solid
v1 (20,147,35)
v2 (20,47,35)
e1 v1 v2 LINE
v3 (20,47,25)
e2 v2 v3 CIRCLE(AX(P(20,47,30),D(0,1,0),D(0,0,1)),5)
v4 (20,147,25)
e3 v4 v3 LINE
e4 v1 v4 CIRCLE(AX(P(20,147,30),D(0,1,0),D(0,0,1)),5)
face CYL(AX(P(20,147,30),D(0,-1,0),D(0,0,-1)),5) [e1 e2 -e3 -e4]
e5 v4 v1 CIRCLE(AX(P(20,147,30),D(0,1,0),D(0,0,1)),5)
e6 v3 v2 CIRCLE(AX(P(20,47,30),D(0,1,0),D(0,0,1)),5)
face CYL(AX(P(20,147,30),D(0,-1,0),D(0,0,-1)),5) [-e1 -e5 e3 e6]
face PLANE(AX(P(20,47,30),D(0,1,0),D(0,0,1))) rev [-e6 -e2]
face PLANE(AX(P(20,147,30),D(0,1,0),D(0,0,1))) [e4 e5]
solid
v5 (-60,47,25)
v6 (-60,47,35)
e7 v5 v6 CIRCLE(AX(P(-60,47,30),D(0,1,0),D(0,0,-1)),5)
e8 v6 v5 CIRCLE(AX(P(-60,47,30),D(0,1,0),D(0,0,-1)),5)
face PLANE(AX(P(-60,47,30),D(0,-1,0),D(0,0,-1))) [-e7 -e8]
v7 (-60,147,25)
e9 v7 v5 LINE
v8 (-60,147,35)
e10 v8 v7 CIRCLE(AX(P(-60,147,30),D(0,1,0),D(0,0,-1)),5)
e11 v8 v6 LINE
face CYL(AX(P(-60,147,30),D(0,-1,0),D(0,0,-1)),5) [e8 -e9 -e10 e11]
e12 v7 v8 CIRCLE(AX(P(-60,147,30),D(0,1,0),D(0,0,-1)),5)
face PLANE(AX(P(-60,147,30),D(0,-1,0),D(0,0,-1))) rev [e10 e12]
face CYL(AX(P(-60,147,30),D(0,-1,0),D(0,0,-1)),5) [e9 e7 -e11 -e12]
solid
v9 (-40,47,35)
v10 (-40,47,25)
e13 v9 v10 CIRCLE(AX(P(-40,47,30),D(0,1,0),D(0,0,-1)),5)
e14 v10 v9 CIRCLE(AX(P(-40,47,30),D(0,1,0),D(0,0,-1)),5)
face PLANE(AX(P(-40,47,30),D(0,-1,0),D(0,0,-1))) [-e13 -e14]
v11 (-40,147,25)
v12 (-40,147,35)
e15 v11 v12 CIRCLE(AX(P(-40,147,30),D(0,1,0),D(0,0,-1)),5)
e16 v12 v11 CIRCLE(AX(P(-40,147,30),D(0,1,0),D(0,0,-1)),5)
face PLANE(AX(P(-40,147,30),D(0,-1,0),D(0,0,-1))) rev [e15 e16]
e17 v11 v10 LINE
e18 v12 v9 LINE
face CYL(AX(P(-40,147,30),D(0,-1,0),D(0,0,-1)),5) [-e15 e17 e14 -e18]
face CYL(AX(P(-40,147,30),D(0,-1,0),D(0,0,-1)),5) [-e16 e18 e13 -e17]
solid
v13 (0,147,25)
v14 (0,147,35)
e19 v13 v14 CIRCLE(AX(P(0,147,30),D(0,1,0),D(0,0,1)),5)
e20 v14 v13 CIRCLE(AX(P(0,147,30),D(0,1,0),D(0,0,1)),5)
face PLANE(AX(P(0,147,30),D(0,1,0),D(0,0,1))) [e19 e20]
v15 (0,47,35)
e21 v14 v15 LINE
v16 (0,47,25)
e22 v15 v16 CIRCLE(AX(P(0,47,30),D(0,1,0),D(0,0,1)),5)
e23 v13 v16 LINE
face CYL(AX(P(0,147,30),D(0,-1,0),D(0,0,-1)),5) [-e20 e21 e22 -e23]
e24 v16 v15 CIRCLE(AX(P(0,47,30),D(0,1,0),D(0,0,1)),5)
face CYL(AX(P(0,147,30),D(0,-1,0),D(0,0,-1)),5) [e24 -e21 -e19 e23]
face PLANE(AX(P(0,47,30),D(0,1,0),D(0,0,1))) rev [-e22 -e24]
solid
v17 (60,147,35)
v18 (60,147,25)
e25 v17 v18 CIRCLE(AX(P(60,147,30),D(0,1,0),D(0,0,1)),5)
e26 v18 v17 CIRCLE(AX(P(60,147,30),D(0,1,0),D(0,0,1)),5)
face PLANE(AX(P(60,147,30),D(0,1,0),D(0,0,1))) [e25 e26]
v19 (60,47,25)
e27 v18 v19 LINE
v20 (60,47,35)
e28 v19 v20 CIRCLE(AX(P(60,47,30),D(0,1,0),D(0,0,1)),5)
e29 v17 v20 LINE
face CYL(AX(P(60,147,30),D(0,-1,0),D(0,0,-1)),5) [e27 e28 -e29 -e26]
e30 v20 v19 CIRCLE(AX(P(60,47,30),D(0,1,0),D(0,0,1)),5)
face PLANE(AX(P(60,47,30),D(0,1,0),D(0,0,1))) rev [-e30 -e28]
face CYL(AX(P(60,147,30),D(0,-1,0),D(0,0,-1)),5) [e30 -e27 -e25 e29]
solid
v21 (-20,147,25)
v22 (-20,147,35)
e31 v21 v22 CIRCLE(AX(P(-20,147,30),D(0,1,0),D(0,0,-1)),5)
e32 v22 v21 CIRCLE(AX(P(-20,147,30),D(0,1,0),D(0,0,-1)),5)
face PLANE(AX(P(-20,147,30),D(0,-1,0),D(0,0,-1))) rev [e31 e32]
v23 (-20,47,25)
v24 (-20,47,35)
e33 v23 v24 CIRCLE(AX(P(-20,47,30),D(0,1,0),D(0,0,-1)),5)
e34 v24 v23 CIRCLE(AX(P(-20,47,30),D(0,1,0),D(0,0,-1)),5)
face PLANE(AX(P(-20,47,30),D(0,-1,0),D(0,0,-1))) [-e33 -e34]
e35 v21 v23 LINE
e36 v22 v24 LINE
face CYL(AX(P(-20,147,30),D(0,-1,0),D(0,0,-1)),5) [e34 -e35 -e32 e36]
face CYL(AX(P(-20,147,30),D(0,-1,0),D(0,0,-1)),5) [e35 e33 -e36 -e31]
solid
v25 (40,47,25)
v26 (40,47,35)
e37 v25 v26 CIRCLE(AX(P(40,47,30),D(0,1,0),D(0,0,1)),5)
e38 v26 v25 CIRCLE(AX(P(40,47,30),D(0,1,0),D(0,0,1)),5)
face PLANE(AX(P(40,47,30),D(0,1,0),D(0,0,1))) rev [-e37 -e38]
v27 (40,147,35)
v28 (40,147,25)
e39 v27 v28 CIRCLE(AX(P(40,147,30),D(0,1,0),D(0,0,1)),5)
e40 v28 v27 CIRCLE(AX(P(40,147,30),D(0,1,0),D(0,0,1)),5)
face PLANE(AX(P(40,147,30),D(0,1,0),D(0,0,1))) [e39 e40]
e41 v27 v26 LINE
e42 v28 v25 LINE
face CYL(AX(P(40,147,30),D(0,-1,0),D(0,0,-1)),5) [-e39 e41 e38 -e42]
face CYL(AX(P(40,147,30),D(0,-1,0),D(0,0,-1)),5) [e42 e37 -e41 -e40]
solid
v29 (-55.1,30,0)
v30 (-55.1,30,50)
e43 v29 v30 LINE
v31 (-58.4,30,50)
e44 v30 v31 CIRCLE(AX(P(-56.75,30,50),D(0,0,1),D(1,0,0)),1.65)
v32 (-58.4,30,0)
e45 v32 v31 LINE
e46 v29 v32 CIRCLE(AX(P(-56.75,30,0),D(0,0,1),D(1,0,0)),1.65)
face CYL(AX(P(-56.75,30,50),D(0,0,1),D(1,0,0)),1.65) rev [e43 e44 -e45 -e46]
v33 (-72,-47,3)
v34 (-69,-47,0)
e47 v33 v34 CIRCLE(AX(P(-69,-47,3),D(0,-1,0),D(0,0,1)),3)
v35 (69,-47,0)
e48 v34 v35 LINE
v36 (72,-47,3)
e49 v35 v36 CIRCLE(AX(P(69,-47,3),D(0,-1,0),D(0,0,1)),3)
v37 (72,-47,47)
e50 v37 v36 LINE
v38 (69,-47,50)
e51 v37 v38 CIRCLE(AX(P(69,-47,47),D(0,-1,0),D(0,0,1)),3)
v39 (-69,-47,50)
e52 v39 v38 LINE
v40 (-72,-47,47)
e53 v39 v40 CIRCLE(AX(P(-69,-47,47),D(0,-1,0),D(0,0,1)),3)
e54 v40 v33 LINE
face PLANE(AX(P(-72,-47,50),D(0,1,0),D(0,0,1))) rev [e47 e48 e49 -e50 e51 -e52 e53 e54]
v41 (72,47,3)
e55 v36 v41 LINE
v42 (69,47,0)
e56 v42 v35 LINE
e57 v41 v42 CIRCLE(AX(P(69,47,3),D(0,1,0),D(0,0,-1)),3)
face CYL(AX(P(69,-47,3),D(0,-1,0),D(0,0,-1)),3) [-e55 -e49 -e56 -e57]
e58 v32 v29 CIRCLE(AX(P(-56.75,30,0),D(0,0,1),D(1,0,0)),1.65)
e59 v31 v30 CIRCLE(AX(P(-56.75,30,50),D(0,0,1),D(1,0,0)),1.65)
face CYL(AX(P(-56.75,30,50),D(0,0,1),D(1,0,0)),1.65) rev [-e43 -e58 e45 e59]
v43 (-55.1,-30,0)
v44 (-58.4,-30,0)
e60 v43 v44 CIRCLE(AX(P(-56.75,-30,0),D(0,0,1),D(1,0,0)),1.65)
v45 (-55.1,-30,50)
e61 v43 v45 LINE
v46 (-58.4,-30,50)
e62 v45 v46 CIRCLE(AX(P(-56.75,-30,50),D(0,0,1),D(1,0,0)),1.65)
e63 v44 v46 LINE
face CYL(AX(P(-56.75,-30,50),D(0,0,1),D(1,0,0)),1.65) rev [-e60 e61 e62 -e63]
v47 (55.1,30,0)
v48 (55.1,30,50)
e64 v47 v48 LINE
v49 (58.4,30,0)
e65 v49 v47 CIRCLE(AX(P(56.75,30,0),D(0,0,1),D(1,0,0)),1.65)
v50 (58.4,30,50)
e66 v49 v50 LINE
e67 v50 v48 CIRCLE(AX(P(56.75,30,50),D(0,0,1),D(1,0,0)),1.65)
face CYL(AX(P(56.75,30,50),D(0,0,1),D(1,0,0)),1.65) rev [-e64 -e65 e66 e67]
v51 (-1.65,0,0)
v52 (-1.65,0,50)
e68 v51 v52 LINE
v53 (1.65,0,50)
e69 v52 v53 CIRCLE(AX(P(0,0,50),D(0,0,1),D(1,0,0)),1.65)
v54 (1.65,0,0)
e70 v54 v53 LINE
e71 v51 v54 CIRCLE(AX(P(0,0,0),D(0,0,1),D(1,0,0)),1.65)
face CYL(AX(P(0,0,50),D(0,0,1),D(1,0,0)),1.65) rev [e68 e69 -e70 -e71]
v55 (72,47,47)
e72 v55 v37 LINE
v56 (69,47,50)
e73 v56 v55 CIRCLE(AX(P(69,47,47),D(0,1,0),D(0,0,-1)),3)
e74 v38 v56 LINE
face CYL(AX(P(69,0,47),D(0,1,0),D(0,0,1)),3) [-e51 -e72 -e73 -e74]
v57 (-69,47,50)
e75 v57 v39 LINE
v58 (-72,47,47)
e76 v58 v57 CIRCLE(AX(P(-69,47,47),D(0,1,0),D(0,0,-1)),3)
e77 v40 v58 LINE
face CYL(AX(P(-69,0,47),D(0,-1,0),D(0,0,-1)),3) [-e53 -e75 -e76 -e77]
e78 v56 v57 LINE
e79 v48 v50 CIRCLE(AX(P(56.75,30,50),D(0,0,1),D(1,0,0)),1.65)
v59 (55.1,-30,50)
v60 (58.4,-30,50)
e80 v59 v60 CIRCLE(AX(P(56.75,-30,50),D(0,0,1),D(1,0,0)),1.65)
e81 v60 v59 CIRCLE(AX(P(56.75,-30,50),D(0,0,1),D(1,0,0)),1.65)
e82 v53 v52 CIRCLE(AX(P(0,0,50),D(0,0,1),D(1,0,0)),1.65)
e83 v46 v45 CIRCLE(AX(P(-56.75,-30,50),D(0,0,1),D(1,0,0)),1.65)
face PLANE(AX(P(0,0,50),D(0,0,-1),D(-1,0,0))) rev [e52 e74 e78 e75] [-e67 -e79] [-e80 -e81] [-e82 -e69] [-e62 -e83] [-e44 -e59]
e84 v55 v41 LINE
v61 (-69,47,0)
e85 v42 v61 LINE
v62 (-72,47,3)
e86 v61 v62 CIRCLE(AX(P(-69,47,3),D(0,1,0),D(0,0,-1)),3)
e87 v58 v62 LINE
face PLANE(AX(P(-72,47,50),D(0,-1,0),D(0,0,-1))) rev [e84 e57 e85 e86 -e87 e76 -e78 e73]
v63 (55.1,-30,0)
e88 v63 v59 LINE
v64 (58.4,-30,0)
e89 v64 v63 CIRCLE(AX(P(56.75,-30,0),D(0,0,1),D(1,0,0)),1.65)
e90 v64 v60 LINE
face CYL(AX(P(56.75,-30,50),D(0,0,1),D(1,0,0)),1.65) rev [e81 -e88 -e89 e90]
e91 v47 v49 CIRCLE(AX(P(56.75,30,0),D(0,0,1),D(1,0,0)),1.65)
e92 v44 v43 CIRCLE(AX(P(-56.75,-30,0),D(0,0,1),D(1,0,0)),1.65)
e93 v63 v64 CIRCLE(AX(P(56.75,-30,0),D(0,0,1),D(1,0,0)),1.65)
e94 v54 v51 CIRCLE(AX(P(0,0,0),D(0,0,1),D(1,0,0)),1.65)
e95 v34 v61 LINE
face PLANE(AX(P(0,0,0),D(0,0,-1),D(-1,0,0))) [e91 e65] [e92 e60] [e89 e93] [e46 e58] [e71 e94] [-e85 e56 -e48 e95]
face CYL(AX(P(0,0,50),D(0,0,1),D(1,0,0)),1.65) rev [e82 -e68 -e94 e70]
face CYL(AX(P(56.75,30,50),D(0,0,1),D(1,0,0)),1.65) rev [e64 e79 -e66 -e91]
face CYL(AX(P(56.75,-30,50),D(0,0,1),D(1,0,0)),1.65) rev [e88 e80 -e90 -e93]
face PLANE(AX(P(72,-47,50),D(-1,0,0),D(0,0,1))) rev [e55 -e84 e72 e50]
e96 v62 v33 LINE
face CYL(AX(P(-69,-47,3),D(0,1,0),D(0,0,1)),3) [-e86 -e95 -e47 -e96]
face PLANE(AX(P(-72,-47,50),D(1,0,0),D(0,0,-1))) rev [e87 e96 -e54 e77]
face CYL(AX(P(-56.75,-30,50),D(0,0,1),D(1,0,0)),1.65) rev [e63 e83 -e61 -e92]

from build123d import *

# Parameters (mm, degrees)
SKETCH_1_W                  = 144
SKETCH_1_H                  = 94
EXTRUDE_1_DEPTH             = 50
SKETCH_2_R                  = 5
EXTRUDE_2_DEPTH             = 100
EXTRUDE_2_2_DEPTH           = 100
EXTRUDE_2_3_DEPTH           = 100
EXTRUDE_2_4_DEPTH           = 100
EXTRUDE_2_5_DEPTH           = 100
EXTRUDE_2_6_DEPTH           = 100
EXTRUDE_2_7_DEPTH           = 100
FILLET_1_R                  = 3
SKETCH_4_W                  = 1.65
SKETCH_4_H                  = 50
HOLE_WIZARD_M4_1_AT_2_COUNT = 2
HOLE_WIZARD_M4_1_AT_2_PITCH = 64.191607707
HOLE_WIZARD_M4_1_AT_3_COUNT = 2
HOLE_WIZARD_M4_1_AT_3_PITCH = 113.5
HOLE_WIZARD_M4_1_AT_4_COUNT = 2
HOLE_WIZARD_M4_1_AT_4_PITCH = 60
HOLE_WIZARD_M4_1_AT_5_COUNT = 2
HOLE_WIZARD_M4_1_AT_5_PITCH = 128.383215414


with BuildPart() as part:
    # 草图1 → 凸台-拉伸1 (new body)
    with BuildSketch(Plane.XY):
        Rectangle(SKETCH_1_W, SKETCH_1_H)
    extrude(amount=EXTRUDE_1_DEPTH)

    # 圆角1
    fillet_1_edges = [part.edges().sort_by_distance(p)[0] for p in [
        (-72, 0, 50),
        (72, 0, 50),
        (-72, 0, 0),
        (72, 0, 0),
    ]]
    fillet(fillet_1_edges, radius=FILLET_1_R)

    # 草图4 → M4 螺纹孔1 (revolve, cut)
    with BuildSketch(Plane(origin=(-56.75, 30, 50), x_dir=(0, -1, 0), z_dir=(1, 0, 0))):
        with Locations((0.825, 25)):
            Rectangle(SKETCH_4_W, SKETCH_4_H)
    hole_wizard_m4_1 = revolve(axis=Axis((-56.75, 30, 56.35), (0, 0, -1)), mode=Mode.SUBTRACT)

    # M4 螺纹孔1 at 2: M4 螺纹孔1 ×2
    with Locations(*[Vector(0.8840719531297252, -0.46735081222716746, 0) * (i * HOLE_WIZARD_M4_1_AT_2_PITCH) for i in range(1, HOLE_WIZARD_M4_1_AT_2_COUNT)]):
        add(hole_wizard_m4_1, mode=Mode.SUBTRACT)

    # M4 螺纹孔1 at 3: M4 螺纹孔1 ×2
    with Locations(*[(i * HOLE_WIZARD_M4_1_AT_3_PITCH, 0, 0) for i in range(1, HOLE_WIZARD_M4_1_AT_3_COUNT)]):
        add(hole_wizard_m4_1, mode=Mode.SUBTRACT)

    # M4 螺纹孔1 at 4: M4 螺纹孔1 ×2
    with Locations(*[(0, -i * HOLE_WIZARD_M4_1_AT_4_PITCH, 0) for i in range(1, HOLE_WIZARD_M4_1_AT_4_COUNT)]):
        add(hole_wizard_m4_1, mode=Mode.SUBTRACT)

    # M4 螺纹孔1 at 5: M4 螺纹孔1 ×2
    with Locations(*[Vector(0.8840719531297252, -0.46735081222716734, 0) * (i * HOLE_WIZARD_M4_1_AT_5_PITCH) for i in range(1, HOLE_WIZARD_M4_1_AT_5_COUNT)]):
        add(hole_wizard_m4_1, mode=Mode.SUBTRACT)


with BuildPart() as body_2:
    # 草图2 → 凸台-拉伸2 (new body)
    with BuildSketch(Plane(origin=(0, 47, 0), x_dir=(1, 0, 0), z_dir=(0, 1, 0))):
        with Locations(Location((0, -30, 0), (0, 0, 90))):
            Circle(SKETCH_2_R)
    extrude(amount=EXTRUDE_2_DEPTH)


with BuildPart() as body_3:
    # 草图2 → Extrude 2 2 (new body)
    with BuildSketch(Plane(origin=(0, 47, 0), x_dir=(1, 0, 0), z_dir=(0, 1, 0))):
        with Locations(Location((20, -30, 0), (0, 0, 90))):
            Circle(SKETCH_2_R)
    extrude(amount=EXTRUDE_2_2_DEPTH)


with BuildPart() as body_4:
    # 草图2 → Extrude 2 3 (new body)
    with BuildSketch(Plane(origin=(0, 47, 0), x_dir=(1, 0, 0), z_dir=(0, 1, 0))):
        with Locations(Location((40, -30, 0), (0, 0, 90))):
            Circle(SKETCH_2_R)
    extrude(amount=EXTRUDE_2_3_DEPTH)


with BuildPart() as body_5:
    # 草图2 → Extrude 2 4 (new body)
    with BuildSketch(Plane(origin=(0, 47, 0), x_dir=(1, 0, 0), z_dir=(0, 1, 0))):
        with Locations(Location((60, -30, 0), (0, 0, 90))):
            Circle(SKETCH_2_R)
    extrude(amount=EXTRUDE_2_4_DEPTH)


with BuildPart() as body_6:
    # 草图2 → Extrude 2 5 (new body)
    with BuildSketch(Plane(origin=(0, 47, 0), x_dir=(1, 0, 0), z_dir=(0, 1, 0))):
        with Locations(Location((-60, -30, 0), (0, 0, 90))):
            Circle(SKETCH_2_R)
    extrude(amount=EXTRUDE_2_5_DEPTH)


with BuildPart() as body_7:
    # 草图2 → Extrude 2 6 (new body)
    with BuildSketch(Plane(origin=(0, 47, 0), x_dir=(1, 0, 0), z_dir=(0, 1, 0))):
        with Locations(Location((-40, -30, 0), (0, 0, 90))):
            Circle(SKETCH_2_R)
    extrude(amount=EXTRUDE_2_6_DEPTH)


with BuildPart() as body_8:
    # 草图2 → Extrude 2 7 (new body)
    with BuildSketch(Plane(origin=(0, 47, 0), x_dir=(1, 0, 0), z_dir=(0, 1, 0))):
        with Locations(Location((-20, -30, 0), (0, 0, 90))):
            Circle(SKETCH_2_R)
    extrude(amount=EXTRUDE_2_7_DEPTH)


solid = Compound([part.part, body_2.part, body_3.part, body_4.part, body_5.part, body_6.part, body_7.part, body_8.part])
